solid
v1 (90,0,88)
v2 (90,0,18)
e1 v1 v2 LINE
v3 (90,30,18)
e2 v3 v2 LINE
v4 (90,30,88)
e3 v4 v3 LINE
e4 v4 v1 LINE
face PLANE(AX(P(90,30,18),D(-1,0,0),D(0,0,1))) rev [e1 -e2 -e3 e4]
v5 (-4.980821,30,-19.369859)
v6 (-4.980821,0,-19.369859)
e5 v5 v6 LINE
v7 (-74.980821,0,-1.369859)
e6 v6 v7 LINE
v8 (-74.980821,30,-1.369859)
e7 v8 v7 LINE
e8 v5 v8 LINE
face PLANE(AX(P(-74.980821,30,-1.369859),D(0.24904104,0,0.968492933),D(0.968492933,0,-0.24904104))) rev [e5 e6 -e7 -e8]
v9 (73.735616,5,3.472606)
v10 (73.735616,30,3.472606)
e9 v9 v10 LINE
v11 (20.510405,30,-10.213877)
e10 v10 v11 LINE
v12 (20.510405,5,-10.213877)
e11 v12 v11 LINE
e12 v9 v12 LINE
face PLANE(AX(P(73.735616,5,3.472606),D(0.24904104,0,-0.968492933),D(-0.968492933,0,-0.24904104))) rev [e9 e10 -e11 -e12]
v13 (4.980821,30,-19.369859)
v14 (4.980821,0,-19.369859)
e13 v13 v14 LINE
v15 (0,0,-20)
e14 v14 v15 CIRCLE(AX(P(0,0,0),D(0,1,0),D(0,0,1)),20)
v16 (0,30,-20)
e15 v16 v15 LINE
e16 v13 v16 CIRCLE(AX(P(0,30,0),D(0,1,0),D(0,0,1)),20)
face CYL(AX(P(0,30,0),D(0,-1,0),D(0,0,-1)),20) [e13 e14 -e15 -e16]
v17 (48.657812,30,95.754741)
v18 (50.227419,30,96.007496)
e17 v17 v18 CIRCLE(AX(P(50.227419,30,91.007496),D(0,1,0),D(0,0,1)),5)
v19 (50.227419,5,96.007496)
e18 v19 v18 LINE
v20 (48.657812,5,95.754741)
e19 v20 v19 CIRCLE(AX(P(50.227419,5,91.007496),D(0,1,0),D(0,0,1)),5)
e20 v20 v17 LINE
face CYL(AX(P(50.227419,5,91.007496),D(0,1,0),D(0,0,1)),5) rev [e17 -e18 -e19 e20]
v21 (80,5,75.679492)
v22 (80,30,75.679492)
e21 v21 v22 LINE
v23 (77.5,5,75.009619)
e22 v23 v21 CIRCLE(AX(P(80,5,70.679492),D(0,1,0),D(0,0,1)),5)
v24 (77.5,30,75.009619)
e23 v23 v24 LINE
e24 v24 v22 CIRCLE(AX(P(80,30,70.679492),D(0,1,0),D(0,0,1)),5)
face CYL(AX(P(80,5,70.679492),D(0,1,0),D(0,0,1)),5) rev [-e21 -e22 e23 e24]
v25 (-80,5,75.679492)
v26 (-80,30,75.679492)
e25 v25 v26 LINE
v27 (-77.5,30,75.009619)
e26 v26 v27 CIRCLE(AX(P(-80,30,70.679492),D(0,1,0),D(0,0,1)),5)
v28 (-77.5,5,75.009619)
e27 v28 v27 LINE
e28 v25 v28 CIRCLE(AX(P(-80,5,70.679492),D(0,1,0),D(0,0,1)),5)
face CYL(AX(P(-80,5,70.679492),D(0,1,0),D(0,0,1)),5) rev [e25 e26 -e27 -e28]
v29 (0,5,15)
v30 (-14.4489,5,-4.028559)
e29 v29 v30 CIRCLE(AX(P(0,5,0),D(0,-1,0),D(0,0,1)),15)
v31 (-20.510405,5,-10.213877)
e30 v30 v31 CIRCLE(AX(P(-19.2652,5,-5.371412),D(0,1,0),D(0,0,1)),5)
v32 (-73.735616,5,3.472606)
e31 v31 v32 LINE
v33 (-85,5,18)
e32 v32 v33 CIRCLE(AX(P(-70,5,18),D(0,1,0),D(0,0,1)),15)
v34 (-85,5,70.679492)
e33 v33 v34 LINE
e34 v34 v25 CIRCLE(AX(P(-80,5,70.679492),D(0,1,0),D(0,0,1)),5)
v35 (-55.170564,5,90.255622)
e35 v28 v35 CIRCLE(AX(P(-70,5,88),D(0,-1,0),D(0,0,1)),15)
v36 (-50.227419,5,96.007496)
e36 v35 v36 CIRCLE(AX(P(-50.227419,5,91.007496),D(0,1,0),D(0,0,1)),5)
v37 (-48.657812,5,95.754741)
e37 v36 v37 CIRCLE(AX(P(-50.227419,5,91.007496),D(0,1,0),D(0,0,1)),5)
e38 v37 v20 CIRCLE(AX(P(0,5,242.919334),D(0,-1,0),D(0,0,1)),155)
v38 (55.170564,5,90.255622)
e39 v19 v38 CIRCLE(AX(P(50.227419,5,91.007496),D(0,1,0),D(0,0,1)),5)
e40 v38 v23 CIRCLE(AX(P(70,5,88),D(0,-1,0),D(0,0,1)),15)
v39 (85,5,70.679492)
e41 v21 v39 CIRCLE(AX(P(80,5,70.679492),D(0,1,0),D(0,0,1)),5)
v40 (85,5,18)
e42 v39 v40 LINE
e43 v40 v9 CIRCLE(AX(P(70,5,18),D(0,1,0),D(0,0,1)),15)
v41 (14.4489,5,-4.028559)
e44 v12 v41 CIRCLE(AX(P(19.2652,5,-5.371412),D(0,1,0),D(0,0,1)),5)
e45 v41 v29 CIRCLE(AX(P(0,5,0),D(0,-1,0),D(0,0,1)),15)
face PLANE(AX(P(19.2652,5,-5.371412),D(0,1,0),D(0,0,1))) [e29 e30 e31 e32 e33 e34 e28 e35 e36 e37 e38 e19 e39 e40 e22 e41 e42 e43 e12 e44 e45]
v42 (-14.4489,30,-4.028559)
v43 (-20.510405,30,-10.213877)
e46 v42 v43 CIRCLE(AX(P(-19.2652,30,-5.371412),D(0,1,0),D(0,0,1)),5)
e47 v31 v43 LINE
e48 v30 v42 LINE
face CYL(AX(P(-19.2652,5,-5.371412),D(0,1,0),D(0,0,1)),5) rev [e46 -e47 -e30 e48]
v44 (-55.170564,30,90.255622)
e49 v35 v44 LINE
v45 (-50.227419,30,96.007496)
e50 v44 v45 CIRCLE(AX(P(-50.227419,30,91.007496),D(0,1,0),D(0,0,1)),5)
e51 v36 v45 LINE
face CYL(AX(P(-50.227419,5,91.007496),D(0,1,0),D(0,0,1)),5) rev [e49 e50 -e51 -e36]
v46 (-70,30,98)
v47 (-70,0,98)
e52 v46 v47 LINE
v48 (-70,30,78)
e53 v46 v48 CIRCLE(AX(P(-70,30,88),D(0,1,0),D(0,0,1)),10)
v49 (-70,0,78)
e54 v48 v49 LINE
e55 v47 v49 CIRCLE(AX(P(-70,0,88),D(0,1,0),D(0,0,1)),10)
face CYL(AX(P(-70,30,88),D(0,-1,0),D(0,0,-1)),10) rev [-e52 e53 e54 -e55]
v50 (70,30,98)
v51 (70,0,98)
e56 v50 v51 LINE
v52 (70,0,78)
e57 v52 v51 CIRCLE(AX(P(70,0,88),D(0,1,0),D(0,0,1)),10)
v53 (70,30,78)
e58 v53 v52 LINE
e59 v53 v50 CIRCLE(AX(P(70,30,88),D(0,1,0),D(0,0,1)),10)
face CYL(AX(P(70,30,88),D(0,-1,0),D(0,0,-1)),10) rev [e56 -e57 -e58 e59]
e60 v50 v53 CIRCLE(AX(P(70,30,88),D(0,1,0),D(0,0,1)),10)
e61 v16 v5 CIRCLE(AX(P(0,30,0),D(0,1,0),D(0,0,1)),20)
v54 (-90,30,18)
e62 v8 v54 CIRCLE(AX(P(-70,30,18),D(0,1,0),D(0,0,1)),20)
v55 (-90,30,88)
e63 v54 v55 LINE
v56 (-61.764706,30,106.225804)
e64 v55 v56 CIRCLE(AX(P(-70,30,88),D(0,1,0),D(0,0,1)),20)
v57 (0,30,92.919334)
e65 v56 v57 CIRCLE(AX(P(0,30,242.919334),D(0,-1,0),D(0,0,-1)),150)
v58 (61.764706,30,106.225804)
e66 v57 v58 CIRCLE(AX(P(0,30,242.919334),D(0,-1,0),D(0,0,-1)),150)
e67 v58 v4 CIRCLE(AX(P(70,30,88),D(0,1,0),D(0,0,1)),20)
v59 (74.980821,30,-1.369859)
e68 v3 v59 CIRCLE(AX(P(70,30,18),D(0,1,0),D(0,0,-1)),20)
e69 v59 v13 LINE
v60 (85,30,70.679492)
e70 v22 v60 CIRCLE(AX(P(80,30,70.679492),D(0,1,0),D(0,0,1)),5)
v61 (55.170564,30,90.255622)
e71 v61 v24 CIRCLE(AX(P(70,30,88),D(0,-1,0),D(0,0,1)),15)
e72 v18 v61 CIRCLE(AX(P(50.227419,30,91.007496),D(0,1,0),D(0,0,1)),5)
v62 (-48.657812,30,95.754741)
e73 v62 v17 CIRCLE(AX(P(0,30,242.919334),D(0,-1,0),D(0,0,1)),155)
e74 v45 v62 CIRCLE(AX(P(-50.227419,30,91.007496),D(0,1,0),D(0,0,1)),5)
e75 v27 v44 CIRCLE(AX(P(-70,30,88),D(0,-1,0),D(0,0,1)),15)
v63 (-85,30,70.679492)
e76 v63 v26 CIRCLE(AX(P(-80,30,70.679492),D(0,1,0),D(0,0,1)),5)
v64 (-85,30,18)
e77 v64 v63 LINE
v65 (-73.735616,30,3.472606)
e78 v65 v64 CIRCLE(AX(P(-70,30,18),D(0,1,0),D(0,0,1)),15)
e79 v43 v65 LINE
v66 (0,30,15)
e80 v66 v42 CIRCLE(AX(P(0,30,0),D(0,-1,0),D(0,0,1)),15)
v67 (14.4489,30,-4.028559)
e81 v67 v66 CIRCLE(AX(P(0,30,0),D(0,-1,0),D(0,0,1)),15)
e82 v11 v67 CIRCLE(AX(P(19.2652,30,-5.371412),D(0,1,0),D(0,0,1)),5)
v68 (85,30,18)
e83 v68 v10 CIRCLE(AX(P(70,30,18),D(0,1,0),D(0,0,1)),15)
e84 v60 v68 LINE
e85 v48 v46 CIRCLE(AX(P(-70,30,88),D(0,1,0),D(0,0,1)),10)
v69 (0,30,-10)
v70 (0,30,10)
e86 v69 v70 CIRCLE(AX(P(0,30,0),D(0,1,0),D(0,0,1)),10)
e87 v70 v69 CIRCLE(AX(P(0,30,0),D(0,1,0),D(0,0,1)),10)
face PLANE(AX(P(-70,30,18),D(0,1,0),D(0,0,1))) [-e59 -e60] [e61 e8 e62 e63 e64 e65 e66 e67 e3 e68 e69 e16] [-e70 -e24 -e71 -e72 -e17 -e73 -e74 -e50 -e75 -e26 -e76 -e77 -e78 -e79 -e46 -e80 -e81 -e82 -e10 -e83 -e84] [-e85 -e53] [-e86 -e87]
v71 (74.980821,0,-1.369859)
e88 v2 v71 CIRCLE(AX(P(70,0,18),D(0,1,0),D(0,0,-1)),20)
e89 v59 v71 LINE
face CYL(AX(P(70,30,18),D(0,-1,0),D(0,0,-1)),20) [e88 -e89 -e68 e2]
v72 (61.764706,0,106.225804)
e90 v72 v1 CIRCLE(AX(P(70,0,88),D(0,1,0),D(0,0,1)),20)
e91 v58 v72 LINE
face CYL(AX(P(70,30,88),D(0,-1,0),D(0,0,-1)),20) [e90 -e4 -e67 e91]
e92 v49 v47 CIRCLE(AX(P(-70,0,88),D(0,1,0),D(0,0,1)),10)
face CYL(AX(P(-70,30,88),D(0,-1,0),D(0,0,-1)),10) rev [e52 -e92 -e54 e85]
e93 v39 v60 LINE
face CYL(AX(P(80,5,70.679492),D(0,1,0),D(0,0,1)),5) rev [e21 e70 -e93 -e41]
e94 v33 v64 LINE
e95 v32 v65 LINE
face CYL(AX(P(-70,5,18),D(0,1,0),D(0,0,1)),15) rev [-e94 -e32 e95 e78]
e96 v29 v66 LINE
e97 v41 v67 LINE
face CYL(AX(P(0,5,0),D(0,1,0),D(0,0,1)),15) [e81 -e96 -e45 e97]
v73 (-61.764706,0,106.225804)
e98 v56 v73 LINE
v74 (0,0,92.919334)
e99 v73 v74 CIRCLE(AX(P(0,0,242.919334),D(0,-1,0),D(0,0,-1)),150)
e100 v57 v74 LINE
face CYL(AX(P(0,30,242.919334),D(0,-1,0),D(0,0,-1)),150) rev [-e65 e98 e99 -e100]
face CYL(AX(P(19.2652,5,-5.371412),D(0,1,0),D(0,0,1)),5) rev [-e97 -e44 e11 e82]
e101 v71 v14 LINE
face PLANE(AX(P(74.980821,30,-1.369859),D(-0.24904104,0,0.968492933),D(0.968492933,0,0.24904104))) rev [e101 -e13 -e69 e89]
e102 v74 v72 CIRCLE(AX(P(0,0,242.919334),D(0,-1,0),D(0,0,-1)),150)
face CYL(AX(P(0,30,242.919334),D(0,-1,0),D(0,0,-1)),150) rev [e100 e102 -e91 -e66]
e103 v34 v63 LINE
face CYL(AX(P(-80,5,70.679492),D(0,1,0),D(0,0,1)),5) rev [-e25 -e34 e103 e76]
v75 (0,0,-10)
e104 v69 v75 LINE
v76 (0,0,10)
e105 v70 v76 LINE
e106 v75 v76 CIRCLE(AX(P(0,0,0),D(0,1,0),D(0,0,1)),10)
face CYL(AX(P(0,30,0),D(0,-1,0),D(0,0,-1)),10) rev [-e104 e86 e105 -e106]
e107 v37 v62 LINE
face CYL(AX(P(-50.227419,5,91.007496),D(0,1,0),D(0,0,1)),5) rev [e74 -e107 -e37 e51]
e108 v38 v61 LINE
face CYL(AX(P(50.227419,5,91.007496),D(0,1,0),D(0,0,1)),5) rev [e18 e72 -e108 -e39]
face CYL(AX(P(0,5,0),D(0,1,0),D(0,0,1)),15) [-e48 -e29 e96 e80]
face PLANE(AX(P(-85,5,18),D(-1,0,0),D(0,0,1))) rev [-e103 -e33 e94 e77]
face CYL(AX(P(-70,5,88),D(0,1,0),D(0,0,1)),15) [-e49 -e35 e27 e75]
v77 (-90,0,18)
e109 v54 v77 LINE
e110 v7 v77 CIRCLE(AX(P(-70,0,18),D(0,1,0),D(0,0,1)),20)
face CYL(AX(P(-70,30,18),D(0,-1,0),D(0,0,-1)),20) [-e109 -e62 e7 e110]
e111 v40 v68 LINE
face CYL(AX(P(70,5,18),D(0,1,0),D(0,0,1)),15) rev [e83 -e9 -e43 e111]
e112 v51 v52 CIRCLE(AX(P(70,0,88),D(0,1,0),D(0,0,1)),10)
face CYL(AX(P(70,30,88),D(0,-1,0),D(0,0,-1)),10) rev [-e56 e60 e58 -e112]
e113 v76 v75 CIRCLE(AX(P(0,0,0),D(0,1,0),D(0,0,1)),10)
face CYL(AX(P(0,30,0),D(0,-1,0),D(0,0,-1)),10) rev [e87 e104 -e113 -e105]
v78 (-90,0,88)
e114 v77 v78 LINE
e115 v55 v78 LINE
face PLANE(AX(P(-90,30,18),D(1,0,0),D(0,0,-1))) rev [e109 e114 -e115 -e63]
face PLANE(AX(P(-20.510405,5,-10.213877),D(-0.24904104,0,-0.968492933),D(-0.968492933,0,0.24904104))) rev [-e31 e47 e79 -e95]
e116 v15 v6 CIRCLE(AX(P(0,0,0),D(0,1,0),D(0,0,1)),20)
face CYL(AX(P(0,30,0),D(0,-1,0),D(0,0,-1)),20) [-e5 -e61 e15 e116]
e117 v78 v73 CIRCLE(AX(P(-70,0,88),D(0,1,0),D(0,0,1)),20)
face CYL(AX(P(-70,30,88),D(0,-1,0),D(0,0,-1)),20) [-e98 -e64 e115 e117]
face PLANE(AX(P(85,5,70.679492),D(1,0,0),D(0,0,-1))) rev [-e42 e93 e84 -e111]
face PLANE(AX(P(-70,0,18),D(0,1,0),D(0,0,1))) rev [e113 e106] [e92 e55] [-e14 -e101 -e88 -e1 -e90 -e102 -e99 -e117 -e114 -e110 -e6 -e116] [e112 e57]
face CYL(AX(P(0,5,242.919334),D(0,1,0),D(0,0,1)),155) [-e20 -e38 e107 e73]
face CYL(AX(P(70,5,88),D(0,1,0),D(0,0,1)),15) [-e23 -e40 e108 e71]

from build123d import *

# Parameters (mm, degrees)
BASE_PLATE_PROFILE_SKETCH_R = 10
BASE_PLATE_30MM_DEPTH       = 30
POCKET_25MM_DEEP_DEPTH      = 25


with BuildPart() as part:
    # Base Plate Profile Sketch → Base Plate 30mm (new body)
    with BuildSketch(Plane(origin=(0, 0, 0), x_dir=(1, 0, 0), z_dir=(0, 1, 0))):
        with BuildLine():
            Line((-74.980820796, 1.369858652), (-4.980820796, 19.369858652))
            ThreePointArc((-4.980820796, 19.369858652), (0, 20), (4.980820796, 19.369858652))
            Line((4.980820796, 19.369858652), (74.980820796, 1.369858652))
            ThreePointArc((74.980820796, 1.369858652), (85.80532214, -5.74472391), (90, -18))
            Line((90, -18), (90, -88))
            ThreePointArc((90, -88), (80.846522891, -104.803361008), (61.764705882, -106.225803982))
            ThreePointArc((61.764705882, -106.225803982), (0, -92.919333848), (-61.764705882, -106.225803982))
            ThreePointArc((-61.764705882, -106.225803982), (-80.846522891, -104.803361008), (-90, -88))
            Line((-90, -88), (-90, -18))
            ThreePointArc((-90, -18), (-85.80532214, -5.74472391), (-74.980820796, 1.369858652))
        make_face()
        with Locations(Location((0, 0, 0), (0, 0, 270))):
            Circle(BASE_PLATE_PROFILE_SKETCH_R, mode=Mode.SUBTRACT)
        with Locations(Location((-70, -88, 0), (0, 0, 270))):
            Circle(BASE_PLATE_PROFILE_SKETCH_R, mode=Mode.SUBTRACT)
        with Locations(Location((70, -88, 0), (0, 0, 270))):
            Circle(BASE_PLATE_PROFILE_SKETCH_R, mode=Mode.SUBTRACT)
    extrude(amount=BASE_PLATE_30MM_DEPTH)

    # Pocket Profile Sketch → Pocket 25mm Deep (cut)
    with BuildSketch(Plane(origin=(0, 30, 0), x_dir=(1, 0, 0), z_dir=(0, 1, 0))):
        with BuildLine():
            Line((-85, -18), (-85, -70.679491924))
            ThreePointArc((-85, -70.679491924), (-82.5, -75.009618943), (-77.5, -75.009618943))
            ThreePointArc((-77.5, -75.009618943), (-61.541849411, -75.612115249), (-55.170564121, -90.255622199))
            ThreePointArc((-55.170564121, -90.255622199), (-53.453138568, -94.827801509), (-48.657811989, -95.75474119))
            ThreePointArc((-48.657811989, -95.75474119), (0, -87.919333848), (48.657811989, -95.75474119))
            ThreePointArc((48.657811989, -95.75474119), (53.453138568, -94.827801509), (55.170564121, -90.255622199))
            ThreePointArc((55.170564121, -90.255622199), (61.541849411, -75.612115249), (77.5, -75.009618943))
            ThreePointArc((77.5, -75.009618943), (82.5, -75.009618943), (85, -70.679491924))
            Line((85, -70.679491924), (85, -18))
            ThreePointArc((85, -18), (81.853991605, -8.808542933), (73.735615597, -3.472606011))
            Line((73.735615597, -3.472606011), (20.510405257, 10.213876648))
            ThreePointArc((20.510405257, 10.213876648), (15.694105243, 8.871023652), (14.448900044, 4.028558989))
            ThreePointArc((14.448900044, 4.028558989), (0, -15), (-14.448900044, 4.028558989))
            ThreePointArc((-14.448900044, 4.028558989), (-15.694105243, 8.871023652), (-20.510405257, 10.213876648))
            Line((-20.510405257, 10.213876648), (-73.735615597, -3.472606011))
            ThreePointArc((-73.735615597, -3.472606011), (-81.853991605, -8.808542933), (-85, -18))
        make_face()
    extrude(amount=-POCKET_25MM_DEEP_DEPTH, mode=Mode.SUBTRACT)


solid = part.part
